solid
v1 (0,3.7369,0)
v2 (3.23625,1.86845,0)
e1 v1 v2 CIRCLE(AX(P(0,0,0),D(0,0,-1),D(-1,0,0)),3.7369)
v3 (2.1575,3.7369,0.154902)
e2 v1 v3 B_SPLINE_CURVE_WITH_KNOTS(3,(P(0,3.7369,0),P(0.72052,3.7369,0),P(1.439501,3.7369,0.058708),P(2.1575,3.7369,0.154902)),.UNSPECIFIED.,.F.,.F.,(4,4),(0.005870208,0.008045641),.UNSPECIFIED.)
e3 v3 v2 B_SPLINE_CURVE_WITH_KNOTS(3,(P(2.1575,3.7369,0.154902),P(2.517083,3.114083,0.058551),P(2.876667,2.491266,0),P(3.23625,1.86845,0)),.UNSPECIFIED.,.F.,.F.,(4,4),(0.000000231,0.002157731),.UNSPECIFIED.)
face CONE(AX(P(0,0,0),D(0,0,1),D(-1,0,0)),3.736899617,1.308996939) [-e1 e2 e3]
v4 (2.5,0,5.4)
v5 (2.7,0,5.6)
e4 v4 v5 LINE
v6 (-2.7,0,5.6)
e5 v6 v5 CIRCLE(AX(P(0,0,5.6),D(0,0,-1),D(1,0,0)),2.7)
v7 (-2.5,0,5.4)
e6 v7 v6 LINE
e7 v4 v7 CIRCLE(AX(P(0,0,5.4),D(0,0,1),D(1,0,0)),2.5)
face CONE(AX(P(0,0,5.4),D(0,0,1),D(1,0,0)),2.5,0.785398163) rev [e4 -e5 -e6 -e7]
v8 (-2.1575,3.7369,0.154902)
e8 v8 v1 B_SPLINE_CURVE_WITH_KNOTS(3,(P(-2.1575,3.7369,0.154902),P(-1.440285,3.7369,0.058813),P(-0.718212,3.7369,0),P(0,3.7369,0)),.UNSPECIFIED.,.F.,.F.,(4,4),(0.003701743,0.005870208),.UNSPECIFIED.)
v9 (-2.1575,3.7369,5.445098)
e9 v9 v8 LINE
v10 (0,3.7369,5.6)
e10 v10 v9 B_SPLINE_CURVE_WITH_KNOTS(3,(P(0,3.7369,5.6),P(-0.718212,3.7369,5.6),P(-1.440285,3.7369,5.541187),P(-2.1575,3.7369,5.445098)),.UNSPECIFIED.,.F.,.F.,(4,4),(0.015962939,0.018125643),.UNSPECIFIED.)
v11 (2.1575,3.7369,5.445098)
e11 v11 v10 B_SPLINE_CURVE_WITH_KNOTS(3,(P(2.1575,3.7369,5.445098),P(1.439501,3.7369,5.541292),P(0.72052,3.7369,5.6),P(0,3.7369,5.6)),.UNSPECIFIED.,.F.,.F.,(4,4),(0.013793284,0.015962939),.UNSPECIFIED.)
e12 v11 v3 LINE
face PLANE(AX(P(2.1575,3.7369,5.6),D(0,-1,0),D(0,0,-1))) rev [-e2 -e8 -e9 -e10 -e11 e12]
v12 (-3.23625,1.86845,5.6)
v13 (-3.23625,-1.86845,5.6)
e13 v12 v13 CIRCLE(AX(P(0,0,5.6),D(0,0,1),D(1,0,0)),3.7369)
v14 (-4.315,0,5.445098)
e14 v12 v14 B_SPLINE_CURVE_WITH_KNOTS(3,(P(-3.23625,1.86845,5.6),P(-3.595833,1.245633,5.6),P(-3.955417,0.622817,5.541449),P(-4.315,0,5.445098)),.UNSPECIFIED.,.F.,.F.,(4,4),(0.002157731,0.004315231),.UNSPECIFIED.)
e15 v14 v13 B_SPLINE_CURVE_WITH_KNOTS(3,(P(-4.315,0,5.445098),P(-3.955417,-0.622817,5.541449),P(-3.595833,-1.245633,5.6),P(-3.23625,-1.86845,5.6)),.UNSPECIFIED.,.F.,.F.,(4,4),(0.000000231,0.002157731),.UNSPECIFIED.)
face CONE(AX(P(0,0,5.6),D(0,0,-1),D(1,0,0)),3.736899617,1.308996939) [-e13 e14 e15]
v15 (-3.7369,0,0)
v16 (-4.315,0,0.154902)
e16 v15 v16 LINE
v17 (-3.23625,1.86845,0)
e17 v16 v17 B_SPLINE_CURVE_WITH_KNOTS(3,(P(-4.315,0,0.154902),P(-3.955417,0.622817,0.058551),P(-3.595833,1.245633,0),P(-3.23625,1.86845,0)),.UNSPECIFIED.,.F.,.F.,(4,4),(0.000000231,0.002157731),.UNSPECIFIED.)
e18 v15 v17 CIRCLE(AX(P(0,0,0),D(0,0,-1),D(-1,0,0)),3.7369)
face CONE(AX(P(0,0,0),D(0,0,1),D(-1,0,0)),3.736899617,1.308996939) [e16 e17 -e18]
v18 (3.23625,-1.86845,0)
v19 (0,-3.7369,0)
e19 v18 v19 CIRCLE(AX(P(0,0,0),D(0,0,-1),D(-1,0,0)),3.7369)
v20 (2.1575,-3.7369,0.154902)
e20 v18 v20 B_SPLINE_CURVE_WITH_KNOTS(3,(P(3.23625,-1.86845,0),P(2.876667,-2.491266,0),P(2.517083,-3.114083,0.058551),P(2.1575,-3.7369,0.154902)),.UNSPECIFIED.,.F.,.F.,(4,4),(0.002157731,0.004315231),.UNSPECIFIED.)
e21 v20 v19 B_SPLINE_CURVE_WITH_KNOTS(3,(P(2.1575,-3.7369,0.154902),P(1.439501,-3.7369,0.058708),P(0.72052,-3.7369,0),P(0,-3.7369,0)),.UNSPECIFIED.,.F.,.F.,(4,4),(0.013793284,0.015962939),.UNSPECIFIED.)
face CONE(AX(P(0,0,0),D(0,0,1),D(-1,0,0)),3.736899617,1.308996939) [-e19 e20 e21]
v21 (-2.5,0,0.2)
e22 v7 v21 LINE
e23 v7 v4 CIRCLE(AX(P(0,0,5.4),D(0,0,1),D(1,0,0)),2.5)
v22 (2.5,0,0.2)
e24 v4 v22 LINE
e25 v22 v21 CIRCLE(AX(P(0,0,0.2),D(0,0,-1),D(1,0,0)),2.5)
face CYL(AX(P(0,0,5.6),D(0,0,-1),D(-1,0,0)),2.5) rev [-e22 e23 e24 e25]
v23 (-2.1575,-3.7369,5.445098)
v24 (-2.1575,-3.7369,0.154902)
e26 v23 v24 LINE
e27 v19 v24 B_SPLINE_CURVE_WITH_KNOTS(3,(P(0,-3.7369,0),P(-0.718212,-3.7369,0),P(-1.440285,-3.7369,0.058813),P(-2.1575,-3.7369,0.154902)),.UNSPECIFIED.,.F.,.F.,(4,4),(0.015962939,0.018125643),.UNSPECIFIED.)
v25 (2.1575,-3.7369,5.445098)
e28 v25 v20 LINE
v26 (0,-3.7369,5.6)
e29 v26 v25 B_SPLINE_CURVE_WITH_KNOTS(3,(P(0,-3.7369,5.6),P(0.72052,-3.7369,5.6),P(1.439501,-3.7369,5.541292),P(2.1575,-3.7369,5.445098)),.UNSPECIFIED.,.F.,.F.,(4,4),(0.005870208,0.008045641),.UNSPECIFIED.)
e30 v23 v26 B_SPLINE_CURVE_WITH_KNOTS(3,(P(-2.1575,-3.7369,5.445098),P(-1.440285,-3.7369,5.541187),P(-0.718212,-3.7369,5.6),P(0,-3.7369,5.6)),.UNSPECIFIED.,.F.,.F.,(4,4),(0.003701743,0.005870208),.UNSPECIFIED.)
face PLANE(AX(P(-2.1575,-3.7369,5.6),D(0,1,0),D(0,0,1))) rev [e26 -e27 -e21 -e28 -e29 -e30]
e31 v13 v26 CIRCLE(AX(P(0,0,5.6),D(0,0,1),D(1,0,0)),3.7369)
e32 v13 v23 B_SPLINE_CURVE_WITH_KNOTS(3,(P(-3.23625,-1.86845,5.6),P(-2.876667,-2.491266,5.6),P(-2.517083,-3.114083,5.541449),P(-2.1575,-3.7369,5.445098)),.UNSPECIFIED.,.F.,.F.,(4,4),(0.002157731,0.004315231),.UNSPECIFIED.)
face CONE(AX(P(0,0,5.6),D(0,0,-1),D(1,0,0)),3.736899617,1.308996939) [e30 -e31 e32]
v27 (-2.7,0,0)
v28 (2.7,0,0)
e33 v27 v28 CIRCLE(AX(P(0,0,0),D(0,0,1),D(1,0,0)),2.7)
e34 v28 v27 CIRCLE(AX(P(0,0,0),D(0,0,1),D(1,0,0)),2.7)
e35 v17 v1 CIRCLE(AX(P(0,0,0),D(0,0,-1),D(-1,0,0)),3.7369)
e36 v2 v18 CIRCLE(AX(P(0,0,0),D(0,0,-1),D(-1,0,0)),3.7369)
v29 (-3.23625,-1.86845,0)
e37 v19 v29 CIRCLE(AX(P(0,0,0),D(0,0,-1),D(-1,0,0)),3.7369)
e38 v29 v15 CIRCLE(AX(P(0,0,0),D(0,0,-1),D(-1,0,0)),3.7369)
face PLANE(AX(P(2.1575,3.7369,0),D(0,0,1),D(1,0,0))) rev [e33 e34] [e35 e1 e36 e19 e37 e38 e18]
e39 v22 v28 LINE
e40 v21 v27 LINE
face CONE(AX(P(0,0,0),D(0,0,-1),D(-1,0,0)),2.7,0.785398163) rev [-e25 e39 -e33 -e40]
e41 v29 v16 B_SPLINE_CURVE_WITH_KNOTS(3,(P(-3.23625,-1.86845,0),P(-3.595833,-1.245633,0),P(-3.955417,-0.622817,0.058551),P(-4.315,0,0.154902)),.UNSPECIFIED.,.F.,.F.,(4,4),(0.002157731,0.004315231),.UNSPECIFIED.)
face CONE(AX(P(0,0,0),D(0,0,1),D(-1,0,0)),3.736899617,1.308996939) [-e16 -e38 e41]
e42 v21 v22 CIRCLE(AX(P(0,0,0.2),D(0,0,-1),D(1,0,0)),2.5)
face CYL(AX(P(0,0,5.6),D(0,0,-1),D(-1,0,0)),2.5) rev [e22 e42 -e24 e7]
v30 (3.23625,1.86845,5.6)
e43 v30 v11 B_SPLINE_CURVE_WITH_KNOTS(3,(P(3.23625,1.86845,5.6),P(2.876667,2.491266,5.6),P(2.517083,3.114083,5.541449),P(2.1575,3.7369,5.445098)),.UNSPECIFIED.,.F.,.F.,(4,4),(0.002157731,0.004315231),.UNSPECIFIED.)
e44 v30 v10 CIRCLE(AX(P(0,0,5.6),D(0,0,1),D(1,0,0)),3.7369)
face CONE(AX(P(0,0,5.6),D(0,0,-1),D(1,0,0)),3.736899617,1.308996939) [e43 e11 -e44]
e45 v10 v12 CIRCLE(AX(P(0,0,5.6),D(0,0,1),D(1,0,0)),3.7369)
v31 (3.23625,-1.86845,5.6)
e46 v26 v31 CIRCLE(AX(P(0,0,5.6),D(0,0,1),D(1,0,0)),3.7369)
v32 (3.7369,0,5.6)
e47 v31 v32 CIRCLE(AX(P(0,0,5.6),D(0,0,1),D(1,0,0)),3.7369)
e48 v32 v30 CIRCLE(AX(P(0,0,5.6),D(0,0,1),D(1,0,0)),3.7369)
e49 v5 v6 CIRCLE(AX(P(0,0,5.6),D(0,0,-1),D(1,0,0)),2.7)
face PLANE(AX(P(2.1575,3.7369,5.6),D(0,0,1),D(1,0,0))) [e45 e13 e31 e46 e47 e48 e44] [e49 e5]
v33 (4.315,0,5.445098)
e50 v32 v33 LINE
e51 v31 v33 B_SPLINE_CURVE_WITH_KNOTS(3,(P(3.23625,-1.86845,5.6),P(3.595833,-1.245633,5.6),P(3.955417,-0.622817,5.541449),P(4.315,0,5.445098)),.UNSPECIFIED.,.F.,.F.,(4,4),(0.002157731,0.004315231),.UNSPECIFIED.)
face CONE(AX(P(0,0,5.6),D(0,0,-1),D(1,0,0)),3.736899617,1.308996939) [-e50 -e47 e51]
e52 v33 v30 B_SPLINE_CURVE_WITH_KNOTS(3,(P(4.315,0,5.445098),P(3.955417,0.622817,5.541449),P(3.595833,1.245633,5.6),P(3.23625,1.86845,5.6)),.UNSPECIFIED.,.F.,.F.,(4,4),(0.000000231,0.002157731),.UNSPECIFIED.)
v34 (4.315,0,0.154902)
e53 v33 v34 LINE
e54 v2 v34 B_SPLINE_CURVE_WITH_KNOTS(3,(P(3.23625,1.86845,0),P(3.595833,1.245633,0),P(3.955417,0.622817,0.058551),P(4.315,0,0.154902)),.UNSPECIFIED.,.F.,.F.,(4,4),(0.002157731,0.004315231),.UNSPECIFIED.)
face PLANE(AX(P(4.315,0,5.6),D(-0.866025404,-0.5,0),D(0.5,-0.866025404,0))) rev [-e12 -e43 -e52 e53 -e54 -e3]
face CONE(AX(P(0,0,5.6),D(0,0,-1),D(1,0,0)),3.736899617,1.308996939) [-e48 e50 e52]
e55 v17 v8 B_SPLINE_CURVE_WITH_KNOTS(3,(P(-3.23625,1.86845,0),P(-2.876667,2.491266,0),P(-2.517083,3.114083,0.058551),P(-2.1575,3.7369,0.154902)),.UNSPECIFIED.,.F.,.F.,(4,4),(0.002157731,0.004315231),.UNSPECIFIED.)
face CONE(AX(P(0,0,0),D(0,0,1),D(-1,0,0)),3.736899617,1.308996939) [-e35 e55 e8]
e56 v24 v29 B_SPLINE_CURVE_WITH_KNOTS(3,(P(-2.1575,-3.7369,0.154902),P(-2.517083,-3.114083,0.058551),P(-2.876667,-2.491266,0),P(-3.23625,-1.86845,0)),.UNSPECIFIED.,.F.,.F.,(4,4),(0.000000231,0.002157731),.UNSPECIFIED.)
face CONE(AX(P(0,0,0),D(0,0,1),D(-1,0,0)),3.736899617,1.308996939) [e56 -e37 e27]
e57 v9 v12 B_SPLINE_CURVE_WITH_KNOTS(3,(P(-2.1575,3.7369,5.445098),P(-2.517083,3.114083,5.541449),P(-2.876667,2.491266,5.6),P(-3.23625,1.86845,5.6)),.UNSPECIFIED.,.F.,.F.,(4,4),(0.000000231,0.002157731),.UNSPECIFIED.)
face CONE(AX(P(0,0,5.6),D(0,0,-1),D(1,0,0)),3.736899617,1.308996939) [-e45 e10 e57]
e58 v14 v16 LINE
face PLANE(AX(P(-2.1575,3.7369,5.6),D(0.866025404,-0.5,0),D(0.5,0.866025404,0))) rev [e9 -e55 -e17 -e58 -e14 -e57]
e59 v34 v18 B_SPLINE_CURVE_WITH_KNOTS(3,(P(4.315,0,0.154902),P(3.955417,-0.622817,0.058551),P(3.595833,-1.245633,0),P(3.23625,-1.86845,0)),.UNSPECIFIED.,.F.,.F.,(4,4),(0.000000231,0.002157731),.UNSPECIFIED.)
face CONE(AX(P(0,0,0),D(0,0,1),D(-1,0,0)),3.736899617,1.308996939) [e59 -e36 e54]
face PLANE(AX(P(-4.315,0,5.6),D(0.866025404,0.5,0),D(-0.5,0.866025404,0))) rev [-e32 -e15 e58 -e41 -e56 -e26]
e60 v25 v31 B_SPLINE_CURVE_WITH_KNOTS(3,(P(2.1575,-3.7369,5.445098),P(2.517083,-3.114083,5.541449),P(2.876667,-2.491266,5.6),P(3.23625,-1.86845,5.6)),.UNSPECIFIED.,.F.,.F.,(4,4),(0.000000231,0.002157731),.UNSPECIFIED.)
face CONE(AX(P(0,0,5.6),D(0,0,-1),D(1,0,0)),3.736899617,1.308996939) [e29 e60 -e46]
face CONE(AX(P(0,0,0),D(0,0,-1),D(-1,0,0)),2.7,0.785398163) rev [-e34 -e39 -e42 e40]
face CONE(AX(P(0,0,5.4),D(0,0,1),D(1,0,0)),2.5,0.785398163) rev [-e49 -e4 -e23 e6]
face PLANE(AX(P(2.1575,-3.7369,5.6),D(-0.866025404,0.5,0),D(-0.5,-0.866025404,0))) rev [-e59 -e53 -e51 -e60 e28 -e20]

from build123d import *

# Parameters (mm, degrees)
SKETCH1_R          = 2.5
BOSS_EXTRUDE_DEPTH = 5.6
SKETCH2_OUTSIDE_W  = 296.81
SKETCH2_OUTSIDE_H  = 295.654
SKETCH2_OUTSIDE_R  = 3.736899617
CUT_EXTRUDE1_DEPTH = 38
CUT_EXTRUDE1_DRAFT = -75
SKETCH3_OUTSIDE_W  = 296.81
SKETCH3_OUTSIDE_H  = 295.654
SKETCH3_OUTSIDE_R  = 3.736899617
CUT_EXTRUDE2_DEPTH = 38
CUT_EXTRUDE2_DRAFT = -75
CHAMFER1_SIZE      = 0.2


with BuildPart() as part:
    # Sketch1 → Boss-Extrude (new body)
    with BuildSketch(Plane.XY):
        Polygon((2.1575, 3.736899617), (-2.1575, 3.736899617), (-4.315, 0), (-2.1575, -3.736899617), (2.1575, -3.736899617), (4.315, 0), align=None)
        Circle(SKETCH1_R, mode=Mode.SUBTRACT)
    extrude(amount=BOSS_EXTRUDE_DEPTH)


with BuildPart() as cut_extrude1_tool:
    # Sketch2 outside → Cut-Extrude1 (with draft: the straight prism first)
    with BuildSketch(Plane(origin=(0, 0, 0), x_dir=(-1, 0, 0), z_dir=(0, 0, -1))):
        Rectangle(SKETCH2_OUTSIDE_W, SKETCH2_OUTSIDE_H)
        Circle(SKETCH2_OUTSIDE_R, mode=Mode.SUBTRACT)
    extrude(amount=-CUT_EXTRUDE1_DEPTH)
    # Cut-Extrude1: the draft: its side faces are tilted about the plane it starts from
    cut_extrude1_sides = [cut_extrude1_tool.faces().sort_by_distance(p)[0] for p in [
        (0, -147.827, 19),
        (-148.405, 0, 19),
        (0, 147.827, 19),
        (148.405, 0, 19),
        (3.736899617, 0, 19),
    ]]
    draft(cut_extrude1_sides, Plane(origin=(0, 0, 0), x_dir=(-1, 0, 0), z_dir=(0, 0, -1)), CUT_EXTRUDE1_DRAFT)


with BuildPart() as part_1:
    add(part.part)

    # Cut-Extrude1: cut by cut_extrude1_tool
    add(cut_extrude1_tool.part, mode=Mode.SUBTRACT)


with BuildPart() as cut_extrude2_tool:
    # Sketch3 outside → Cut-Extrude2 (with draft: the straight prism first)
    with BuildSketch(Plane.XY.offset(5.6)):
        Rectangle(SKETCH3_OUTSIDE_W, SKETCH3_OUTSIDE_H)
        Circle(SKETCH3_OUTSIDE_R, mode=Mode.SUBTRACT)
    extrude(amount=-CUT_EXTRUDE2_DEPTH)
    # Cut-Extrude2: the draft: its side faces are tilted about the plane it starts from
    cut_extrude2_sides = [cut_extrude2_tool.faces().sort_by_distance(p)[0] for p in [
        (0, -147.827, -13.4),
        (148.405, 0, -13.4),
        (0, 147.827, -13.4),
        (-148.405, 0, -13.4),
        (-3.736899617, 0, -13.4),
    ]]
    draft(cut_extrude2_sides, Plane.XY.offset(5.6), CUT_EXTRUDE2_DRAFT)


with BuildPart() as part_2:
    add(part_1.part)

    # Cut-Extrude2: cut by cut_extrude2_tool
    add(cut_extrude2_tool.part, mode=Mode.SUBTRACT)

    # Chamfer1
    chamfer1_edges = [part_2.edges().sort_by_distance(p)[0] for p in [
        (-2.5, 0, 0),
        (-2.5, 0, 5.6),
    ]]
    chamfer(chamfer1_edges, length=CHAMFER1_SIZE)


solid = part_2.part
